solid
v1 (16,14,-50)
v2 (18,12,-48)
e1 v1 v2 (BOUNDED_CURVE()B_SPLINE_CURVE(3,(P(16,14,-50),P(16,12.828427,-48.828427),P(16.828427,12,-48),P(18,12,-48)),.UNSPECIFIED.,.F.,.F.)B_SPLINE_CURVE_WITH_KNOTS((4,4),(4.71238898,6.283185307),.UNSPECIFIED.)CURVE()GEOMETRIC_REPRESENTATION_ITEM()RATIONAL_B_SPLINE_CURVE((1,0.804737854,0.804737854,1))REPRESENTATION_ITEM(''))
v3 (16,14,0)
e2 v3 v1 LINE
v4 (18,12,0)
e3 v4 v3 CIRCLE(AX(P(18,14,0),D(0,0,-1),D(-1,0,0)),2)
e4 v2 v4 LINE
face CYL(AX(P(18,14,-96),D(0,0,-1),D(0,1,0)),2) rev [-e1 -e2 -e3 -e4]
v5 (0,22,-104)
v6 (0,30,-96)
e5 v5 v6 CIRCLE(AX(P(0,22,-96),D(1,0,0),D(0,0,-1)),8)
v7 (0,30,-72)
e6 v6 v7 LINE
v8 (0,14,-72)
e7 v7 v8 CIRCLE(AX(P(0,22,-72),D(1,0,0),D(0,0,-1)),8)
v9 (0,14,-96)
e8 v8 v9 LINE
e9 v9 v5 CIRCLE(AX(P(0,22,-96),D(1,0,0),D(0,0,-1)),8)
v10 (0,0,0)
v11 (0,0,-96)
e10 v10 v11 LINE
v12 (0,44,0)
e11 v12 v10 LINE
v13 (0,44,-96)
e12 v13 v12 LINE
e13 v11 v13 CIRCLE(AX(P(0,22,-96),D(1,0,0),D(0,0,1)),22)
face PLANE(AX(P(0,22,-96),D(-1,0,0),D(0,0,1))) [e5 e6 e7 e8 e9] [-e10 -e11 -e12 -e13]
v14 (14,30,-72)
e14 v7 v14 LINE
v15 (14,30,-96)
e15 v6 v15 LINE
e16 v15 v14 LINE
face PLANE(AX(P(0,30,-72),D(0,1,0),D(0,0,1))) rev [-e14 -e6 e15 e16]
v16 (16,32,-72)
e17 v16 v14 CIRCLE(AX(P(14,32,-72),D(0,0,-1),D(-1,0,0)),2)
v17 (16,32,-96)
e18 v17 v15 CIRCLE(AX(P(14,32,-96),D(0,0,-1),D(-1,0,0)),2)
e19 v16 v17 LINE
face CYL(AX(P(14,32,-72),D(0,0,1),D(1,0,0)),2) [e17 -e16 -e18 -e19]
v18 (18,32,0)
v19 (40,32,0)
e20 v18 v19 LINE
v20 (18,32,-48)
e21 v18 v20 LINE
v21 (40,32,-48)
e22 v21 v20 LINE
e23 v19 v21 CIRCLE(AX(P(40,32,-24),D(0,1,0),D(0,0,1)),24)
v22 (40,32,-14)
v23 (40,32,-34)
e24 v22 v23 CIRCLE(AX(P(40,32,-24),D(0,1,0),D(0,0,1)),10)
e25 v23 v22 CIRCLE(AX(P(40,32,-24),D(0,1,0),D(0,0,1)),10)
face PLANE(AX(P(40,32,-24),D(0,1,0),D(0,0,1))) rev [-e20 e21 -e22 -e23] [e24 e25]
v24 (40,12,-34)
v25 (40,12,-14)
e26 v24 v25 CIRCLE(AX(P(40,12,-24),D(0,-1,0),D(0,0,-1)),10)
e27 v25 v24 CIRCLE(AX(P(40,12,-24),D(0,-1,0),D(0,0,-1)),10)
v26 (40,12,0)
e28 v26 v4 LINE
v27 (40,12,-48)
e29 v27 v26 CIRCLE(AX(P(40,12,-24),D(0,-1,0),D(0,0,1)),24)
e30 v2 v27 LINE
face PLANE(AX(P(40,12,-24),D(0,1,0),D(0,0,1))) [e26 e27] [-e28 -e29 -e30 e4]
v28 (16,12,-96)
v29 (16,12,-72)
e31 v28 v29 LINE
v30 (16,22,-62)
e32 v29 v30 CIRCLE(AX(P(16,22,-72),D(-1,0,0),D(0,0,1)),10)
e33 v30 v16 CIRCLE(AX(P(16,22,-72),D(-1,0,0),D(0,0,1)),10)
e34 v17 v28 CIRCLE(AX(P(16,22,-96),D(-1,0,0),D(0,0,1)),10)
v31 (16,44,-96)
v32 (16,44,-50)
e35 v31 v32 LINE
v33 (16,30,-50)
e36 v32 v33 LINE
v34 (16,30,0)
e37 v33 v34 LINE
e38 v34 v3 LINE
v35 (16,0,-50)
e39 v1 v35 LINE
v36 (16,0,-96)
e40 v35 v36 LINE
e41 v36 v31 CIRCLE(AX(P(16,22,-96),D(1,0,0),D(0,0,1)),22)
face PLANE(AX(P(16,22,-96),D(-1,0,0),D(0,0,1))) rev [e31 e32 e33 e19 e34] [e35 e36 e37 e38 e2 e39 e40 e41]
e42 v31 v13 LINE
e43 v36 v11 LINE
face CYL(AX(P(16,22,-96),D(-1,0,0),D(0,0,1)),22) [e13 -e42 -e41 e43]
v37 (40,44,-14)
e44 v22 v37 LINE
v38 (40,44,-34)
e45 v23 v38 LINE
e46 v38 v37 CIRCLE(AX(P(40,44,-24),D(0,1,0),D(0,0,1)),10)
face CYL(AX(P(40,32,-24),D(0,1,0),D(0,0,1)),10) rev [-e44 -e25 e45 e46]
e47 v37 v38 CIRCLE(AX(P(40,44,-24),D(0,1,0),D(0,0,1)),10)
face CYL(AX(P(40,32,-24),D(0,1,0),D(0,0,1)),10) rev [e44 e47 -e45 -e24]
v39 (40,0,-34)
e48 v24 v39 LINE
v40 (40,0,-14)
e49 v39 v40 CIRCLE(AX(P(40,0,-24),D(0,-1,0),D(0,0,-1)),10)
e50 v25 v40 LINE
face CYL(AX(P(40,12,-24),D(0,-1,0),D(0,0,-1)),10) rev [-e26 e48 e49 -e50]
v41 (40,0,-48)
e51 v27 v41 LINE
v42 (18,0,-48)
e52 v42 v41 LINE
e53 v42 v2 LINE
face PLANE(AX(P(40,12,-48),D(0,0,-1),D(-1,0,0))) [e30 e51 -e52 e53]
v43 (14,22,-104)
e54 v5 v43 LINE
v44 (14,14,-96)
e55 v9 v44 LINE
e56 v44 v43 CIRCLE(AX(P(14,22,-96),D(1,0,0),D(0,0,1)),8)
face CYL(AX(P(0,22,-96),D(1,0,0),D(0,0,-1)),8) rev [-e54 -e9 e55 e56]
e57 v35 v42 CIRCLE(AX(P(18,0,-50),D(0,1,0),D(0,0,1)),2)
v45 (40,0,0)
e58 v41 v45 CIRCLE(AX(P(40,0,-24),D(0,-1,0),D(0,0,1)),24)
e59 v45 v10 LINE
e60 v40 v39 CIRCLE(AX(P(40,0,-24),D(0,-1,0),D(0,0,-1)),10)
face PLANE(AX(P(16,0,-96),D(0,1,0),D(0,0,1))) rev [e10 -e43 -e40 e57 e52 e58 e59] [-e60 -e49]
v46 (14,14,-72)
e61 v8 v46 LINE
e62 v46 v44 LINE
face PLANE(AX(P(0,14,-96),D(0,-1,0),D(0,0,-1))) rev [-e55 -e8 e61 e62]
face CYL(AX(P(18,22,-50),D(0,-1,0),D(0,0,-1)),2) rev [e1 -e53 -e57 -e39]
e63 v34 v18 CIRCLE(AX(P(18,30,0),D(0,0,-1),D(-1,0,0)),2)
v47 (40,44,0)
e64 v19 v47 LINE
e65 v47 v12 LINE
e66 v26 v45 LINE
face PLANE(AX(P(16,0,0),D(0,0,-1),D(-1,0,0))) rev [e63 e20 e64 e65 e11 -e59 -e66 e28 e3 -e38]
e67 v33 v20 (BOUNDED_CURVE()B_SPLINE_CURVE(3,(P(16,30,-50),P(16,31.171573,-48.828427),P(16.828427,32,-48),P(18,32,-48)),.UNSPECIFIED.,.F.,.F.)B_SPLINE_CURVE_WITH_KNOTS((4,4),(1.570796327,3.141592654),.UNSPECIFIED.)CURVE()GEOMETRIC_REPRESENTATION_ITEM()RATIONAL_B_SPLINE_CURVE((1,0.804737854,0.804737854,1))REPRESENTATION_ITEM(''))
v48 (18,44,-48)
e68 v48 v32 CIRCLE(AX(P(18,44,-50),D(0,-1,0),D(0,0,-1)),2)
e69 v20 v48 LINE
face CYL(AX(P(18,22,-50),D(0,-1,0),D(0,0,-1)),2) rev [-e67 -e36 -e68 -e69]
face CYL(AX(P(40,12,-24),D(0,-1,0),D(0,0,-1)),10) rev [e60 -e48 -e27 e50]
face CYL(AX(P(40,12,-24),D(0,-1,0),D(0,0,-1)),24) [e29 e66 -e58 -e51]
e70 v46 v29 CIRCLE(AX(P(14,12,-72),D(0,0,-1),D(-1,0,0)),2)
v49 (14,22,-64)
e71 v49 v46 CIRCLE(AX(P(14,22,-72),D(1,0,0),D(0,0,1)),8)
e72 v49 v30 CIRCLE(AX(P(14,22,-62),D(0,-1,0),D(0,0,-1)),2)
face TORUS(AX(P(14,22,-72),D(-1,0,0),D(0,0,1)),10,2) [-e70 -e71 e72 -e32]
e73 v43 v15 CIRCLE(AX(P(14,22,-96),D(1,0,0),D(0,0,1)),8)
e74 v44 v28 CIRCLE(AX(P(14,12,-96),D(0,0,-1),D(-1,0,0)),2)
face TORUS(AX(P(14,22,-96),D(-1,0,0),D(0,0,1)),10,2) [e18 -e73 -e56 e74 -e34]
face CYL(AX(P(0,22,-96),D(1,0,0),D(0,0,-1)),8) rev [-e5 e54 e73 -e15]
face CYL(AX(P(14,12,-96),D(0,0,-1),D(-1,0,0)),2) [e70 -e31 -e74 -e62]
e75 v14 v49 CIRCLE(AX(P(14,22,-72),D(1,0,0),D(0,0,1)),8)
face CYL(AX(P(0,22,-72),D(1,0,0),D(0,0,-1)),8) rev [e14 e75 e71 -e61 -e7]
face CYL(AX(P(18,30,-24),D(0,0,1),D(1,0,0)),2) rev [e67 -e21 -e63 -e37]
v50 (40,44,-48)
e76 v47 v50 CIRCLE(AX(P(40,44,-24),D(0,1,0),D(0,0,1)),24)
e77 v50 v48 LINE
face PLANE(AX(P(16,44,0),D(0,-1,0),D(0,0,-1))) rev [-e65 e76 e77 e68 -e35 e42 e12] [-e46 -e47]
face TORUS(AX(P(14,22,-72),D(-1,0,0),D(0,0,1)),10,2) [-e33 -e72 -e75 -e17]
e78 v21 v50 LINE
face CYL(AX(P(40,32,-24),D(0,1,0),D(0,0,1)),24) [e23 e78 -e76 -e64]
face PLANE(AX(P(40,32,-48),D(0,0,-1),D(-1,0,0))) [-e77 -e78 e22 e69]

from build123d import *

# Parameters (mm, degrees)
BASE_BLOCK_DEPTH             = 16
BASE_WINDOW_CUT_DEPTH        = 16
FIRST_LUG_DEPTH              = 12
SECOND_START                 = -12
SECOND_LUG_DEPTH             = 12
SECOND_LUG_HOLE_PROFILE_20_R = 10
SECOND_LUG_PIN_HOLE_20_DEPTH = 12
FIRST_START                  = -12
FIRST_LUG_HOLE_PROFILE_20_R  = 10
FIRST_LUG_PIN_HOLE_20_DEPTH  = 12
FIRST_LUG_FILLETS_R2_R       = 2
LUG_JUNCTION_FILLETS_R2_R    = 2
WINDOW_EDGE_FILLETS_R2_R     = 2


with BuildPart() as part:
    # Base Block Profile → Base Block (new body)
    with BuildSketch(Plane(origin=(0, 0, 0), x_dir=(0, 0, -1), z_dir=(1, 0, 0))):
        with BuildLine():
            Line((0, 0), (0, 44))
            Line((0, 44), (96, 44))
            ThreePointArc((96, 44), (118, 22), (96, 0))
            Line((96, 0), (0, 0))
        make_face()
    extrude(amount=BASE_BLOCK_DEPTH)

    # Window Profile → Base Window Cut (cut)
    with BuildSketch(Plane(origin=(16, 0, 0), x_dir=(0, 0, -1), z_dir=(1, 0, 0))):
        with BuildLine():
            Line((72, 30), (96, 30))
            ThreePointArc((96, 30), (104, 22), (96, 14))
            Line((96, 14), (72, 14))
            ThreePointArc((72, 14), (64, 22), (72, 30))
        make_face()
    extrude(amount=-BASE_WINDOW_CUT_DEPTH, mode=Mode.SUBTRACT)

    # First Lug Profile → First Lug (add)
    with BuildSketch(Plane.XZ):
        with BuildLine():
            Line((0, 0), (40, 0))
            ThreePointArc((40, 0), (64, -24), (40, -48))
            Line((40, -48), (0, -48))
            Line((0, -48), (0, 0))
        make_face()
    extrude(amount=-FIRST_LUG_DEPTH)

    # Second Lug Profile → Second Lug (add)
    with BuildSketch(Plane(origin=(0, 44, 0), x_dir=(1, 0, 0), z_dir=(0, 1, 0)).offset(SECOND_START)):
        with BuildLine():
            Line((0, 0), (40, 0))
            ThreePointArc((40, 0), (64, 24), (40, 48))
            Line((40, 48), (0, 48))
            Line((0, 48), (0, 0))
        make_face()
    extrude(amount=SECOND_LUG_DEPTH)

    # Second Lug Hole Profile Ø20 → Second Lug Pin Hole Ø20 (cut)
    with BuildSketch(Plane(origin=(0, 44, 0), x_dir=(1, 0, 0), z_dir=(0, 1, 0))):
        with Locations(Location((40, 24, 0), (0, 0, 270))):
            Circle(SECOND_LUG_HOLE_PROFILE_20_R)
    extrude(amount=-SECOND_LUG_PIN_HOLE_20_DEPTH, mode=Mode.SUBTRACT)

    # First Lug Hole Profile Ø20 → First Lug Pin Hole Ø20 (cut)
    with BuildSketch(Plane.XZ.offset(FIRST_START)):
        with Locations(Location((40, -24, 0), (0, 0, 90))):
            Circle(FIRST_LUG_HOLE_PROFILE_20_R)
    extrude(amount=FIRST_LUG_PIN_HOLE_20_DEPTH, mode=Mode.SUBTRACT)

    # First Lug Fillets R2
    first_lug_fillets_r2_edges = [part.edges().sort_by_distance(p)[0] for p in [
        (16, 6, -48),
    ]]
    fillet(first_lug_fillets_r2_edges, radius=FIRST_LUG_FILLETS_R2_R)

    # Lug Junction Fillets R2
    lug_junction_fillets_r2_edges = [part.edges().sort_by_distance(p)[0] for p in [
        (16, 12, -25),
        (16, 32, -24),
        (16, 38, -48),
    ]]
    fillet(lug_junction_fillets_r2_edges, radius=LUG_JUNCTION_FILLETS_R2_R)

    # Window Edge Fillets R2
    window_edge_fillets_r2_edges = [part.edges().sort_by_distance(p)[0] for p in [
        (16, 22, -64),
        (16, 14, -84),
        (16, 22, -104),
        (16, 30, -84),
    ]]
    fillet(window_edge_fillets_r2_edges, radius=WINDOW_EDGE_FILLETS_R2_R)


solid = part.part
